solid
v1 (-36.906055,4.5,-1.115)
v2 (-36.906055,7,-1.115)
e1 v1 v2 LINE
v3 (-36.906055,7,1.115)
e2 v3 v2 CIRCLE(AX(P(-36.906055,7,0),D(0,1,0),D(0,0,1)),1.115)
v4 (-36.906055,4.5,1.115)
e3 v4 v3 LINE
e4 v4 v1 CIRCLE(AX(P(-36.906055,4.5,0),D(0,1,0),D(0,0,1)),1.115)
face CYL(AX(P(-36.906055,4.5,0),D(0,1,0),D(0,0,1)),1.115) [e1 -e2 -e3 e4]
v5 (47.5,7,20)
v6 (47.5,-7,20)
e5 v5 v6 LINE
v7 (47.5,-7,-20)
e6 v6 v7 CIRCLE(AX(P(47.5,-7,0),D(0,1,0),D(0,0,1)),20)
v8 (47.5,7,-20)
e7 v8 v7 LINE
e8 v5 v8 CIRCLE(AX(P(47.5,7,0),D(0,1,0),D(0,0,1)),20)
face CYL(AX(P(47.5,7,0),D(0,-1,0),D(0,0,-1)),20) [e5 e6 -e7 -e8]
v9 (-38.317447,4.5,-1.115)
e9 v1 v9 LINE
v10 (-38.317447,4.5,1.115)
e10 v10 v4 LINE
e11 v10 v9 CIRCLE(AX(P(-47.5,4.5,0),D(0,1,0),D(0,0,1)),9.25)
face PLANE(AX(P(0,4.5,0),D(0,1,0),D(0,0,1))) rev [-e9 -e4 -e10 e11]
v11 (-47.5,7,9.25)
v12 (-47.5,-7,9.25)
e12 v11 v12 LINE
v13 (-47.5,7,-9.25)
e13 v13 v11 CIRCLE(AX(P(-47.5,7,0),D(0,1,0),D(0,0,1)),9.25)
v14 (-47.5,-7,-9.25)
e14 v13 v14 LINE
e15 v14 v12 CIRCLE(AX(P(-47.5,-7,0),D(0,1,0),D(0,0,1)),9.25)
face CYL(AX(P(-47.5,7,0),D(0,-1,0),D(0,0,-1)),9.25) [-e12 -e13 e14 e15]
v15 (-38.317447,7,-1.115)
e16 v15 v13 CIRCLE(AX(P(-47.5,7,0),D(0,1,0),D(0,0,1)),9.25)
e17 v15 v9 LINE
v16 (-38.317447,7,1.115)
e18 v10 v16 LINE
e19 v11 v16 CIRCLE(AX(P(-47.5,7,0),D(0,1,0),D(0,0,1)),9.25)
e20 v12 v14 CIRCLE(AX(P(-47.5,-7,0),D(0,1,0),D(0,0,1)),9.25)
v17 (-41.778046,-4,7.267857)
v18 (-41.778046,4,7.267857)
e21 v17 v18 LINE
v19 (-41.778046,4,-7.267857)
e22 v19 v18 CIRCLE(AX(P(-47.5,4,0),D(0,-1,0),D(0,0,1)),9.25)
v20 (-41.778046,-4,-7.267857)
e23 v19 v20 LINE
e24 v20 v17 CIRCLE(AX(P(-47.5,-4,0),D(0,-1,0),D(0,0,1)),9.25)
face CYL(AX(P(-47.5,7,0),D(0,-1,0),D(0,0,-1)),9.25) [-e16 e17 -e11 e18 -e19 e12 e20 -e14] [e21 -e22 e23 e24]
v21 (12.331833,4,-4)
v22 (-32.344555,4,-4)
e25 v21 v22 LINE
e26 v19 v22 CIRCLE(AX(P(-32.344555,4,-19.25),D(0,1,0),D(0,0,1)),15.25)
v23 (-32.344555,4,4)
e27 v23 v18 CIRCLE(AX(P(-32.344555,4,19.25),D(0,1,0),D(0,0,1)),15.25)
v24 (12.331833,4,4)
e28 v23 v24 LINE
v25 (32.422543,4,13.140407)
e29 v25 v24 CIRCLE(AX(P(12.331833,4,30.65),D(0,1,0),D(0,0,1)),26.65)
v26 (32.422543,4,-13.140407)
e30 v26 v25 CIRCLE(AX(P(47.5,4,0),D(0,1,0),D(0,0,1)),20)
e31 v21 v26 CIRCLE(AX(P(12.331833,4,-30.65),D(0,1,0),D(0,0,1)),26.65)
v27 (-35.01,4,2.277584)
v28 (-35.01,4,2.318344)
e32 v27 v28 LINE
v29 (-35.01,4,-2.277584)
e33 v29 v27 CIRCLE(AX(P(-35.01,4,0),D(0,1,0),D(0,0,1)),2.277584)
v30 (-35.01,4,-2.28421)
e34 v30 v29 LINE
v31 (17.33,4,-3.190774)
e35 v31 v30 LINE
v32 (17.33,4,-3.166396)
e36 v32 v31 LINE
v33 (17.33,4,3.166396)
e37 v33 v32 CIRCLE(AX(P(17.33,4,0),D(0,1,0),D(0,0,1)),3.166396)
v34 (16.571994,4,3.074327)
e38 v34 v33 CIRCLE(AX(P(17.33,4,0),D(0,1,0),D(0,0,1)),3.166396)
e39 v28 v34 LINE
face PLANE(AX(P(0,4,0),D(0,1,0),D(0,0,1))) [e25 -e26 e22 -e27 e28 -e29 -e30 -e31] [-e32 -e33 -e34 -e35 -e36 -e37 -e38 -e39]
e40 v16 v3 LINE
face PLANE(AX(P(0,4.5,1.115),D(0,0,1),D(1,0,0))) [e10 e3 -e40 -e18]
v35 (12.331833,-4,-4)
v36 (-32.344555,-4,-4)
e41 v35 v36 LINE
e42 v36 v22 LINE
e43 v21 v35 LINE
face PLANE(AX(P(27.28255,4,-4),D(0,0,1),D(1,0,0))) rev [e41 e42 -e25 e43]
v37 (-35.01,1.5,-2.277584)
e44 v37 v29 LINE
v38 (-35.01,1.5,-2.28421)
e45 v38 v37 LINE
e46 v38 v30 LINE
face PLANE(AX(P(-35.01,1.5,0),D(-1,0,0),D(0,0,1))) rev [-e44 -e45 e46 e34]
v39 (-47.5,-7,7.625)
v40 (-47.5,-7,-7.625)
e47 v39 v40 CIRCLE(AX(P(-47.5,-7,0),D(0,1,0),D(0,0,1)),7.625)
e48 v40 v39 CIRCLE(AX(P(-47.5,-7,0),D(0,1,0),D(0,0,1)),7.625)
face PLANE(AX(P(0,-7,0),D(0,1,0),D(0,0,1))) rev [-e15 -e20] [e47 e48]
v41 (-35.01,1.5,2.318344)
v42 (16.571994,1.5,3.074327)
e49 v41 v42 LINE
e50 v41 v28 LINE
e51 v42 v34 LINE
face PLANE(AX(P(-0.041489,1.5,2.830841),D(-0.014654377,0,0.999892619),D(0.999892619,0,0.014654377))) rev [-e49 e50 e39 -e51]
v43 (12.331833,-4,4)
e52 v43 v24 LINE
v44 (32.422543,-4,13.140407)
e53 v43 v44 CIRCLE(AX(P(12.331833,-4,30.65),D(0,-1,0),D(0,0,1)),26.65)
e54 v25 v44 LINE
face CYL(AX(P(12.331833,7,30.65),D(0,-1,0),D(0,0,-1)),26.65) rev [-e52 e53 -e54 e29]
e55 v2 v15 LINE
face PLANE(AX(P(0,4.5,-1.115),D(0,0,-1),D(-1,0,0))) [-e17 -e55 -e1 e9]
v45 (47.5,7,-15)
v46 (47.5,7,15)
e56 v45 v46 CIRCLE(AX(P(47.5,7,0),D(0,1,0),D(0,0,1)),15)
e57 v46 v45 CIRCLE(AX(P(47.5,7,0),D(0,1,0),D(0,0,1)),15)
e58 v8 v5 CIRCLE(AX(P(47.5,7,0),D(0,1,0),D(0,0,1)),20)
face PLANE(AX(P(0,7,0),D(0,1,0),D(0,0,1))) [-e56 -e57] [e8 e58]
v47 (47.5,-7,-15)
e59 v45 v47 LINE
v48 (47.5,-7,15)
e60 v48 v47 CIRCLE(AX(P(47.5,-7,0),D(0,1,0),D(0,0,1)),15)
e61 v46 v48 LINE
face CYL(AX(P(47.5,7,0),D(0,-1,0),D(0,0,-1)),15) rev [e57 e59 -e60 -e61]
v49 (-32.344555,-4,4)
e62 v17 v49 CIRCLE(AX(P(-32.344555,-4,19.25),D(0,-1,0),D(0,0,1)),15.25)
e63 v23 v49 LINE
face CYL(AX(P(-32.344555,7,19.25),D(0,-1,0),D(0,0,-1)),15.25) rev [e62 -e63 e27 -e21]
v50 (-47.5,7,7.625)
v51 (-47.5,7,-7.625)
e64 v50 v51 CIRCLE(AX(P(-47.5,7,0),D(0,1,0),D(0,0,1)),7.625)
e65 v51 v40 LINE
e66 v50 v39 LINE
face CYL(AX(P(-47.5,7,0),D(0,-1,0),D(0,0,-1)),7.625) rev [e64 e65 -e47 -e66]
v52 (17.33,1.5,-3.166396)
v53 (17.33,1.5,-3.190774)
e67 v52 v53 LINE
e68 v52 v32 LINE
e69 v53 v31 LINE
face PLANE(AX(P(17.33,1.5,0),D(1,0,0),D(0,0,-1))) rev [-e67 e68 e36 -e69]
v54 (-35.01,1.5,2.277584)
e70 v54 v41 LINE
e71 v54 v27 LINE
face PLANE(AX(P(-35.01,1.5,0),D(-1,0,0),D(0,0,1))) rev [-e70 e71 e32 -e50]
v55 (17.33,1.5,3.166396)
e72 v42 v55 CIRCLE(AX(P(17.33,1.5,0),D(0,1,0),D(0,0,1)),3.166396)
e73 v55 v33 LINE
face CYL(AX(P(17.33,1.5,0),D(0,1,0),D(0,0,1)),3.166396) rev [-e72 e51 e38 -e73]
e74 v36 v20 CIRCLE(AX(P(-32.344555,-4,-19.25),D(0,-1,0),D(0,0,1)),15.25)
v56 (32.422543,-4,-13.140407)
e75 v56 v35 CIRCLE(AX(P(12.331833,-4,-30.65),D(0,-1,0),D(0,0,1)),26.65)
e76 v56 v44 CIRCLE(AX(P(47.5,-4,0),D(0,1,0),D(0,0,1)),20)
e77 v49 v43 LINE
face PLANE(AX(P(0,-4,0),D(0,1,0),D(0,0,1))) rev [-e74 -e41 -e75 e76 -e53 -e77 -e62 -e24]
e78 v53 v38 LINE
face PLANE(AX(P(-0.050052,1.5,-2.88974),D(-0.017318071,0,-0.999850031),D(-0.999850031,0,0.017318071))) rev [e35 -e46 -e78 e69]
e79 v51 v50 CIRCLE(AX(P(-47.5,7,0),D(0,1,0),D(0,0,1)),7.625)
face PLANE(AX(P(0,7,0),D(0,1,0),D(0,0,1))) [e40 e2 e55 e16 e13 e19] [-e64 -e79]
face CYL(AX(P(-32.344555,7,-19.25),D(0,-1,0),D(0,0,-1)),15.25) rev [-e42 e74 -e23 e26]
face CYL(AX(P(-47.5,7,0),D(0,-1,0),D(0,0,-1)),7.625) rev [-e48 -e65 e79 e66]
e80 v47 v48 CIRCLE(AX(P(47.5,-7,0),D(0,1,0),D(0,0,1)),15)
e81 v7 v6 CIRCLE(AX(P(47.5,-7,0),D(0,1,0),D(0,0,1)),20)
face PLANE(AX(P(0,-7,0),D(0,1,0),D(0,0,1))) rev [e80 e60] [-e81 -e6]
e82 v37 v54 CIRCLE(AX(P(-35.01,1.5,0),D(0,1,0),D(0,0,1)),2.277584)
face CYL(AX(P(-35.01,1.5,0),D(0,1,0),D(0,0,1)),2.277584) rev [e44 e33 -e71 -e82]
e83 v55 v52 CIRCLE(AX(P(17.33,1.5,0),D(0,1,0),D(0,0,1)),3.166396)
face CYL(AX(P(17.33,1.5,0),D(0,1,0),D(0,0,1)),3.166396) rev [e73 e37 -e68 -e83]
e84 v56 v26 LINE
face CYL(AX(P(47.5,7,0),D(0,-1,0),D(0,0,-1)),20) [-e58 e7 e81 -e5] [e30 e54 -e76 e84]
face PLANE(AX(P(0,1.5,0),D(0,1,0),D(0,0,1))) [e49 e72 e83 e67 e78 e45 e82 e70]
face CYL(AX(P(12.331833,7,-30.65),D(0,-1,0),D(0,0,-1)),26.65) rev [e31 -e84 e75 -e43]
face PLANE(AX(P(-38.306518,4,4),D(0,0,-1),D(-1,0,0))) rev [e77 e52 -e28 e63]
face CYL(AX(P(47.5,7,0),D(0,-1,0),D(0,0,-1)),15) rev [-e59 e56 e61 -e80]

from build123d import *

# Parameters (mm, degrees)
BIG_END_EYE_SKETCH_R        = 20
BIG_END_EYE_SKETCH_R_2      = 15
BIG_END_EYE_40_DEPTH        = 7
SMALL_END_EYE_SKETCH_R      = 9.25
SMALL_END_EYE_SKETCH_R_2    = 7.625
SMALL_END_EYE_18_5_DEPTH    = 7
SHANK_DEPTH                 = 4
BIG_END_BLEND_R26_65_A_R    = 26.65
SMALL_END_BLEND_R15_25_A_R  = 15.25
SMALL_END_BLEND_R15_25_B_R  = 15.25
BIG_END_BLEND_R26_65_B_R    = 26.65
SHANK_RECESS_2_5_DEEP_DEPTH = 2.5
SHANK_PAD_2_5_DEPTH         = 2.5


with BuildPart() as part:
    # Big End Eye Sketch → Big End Eye Ø40 (new, symmetric)
    with BuildSketch(Plane(origin=(0, 0, 0), x_dir=(1, 0, 0), z_dir=(0, 1, 0))):
        with Locations(Location((47.5, 0, 0), (0, 0, 270))):
            Circle(BIG_END_EYE_SKETCH_R)
        with Locations(Location((47.5, 0, 0), (0, 0, 270))):
            Circle(BIG_END_EYE_SKETCH_R_2, mode=Mode.SUBTRACT)
    extrude(amount=BIG_END_EYE_40_DEPTH, both=True)



with BuildPart() as body_2:
    # Small End Eye Sketch → Small End Eye Ø18.5 (new, symmetric)
    with BuildSketch(Plane(origin=(0, 0, 0), x_dir=(1, 0, 0), z_dir=(0, 1, 0))):
        with Locations(Location((-47.5, 0, 0), (0, 0, 270))):
            Circle(SMALL_END_EYE_SKETCH_R)
        with Locations(Location((-47.5, 0, 0), (0, 0, 270))):
            Circle(SMALL_END_EYE_SKETCH_R_2, mode=Mode.SUBTRACT)
    extrude(amount=SMALL_END_EYE_18_5_DEPTH, both=True)


with BuildPart() as part_1:
    add(part.part)

    add(body_2.part)  # Shank merges body 2
    # Shank Profile Sketch → Shank (add, symmetric)
    with BuildSketch(Plane(origin=(0, 0, 0), x_dir=(1, 0, 0), z_dir=(0, 1, 0))):
        Polygon((27.282550476, 4), (28.047385708, 4), (28.047385708, -4), (-38.306518326, -4), (-39.375179325, -4), (-39.375179325, 4), align=None)
    extrude(amount=SHANK_DEPTH, both=True)

    # Big End Blend R26.65 A
    big_end_blend_r26_65_a_edges = [part_1.edges().sort_by_distance(p)[0] for p in [
        (27.904082058, 0, -4),
    ]]
    fillet(big_end_blend_r26_65_a_edges, radius=BIG_END_BLEND_R26_65_A_R)

    # Small End Blend R15.25 A
    small_end_blend_r15_25_a_edges = [part_1.edges().sort_by_distance(p)[0] for p in [
        (-39.159586341, 0, -4),
    ]]
    fillet(small_end_blend_r15_25_a_edges, radius=SMALL_END_BLEND_R15_25_A_R)

    # Small End Blend R15.25 B
    small_end_blend_r15_25_b_edges = [part_1.edges().sort_by_distance(p)[0] for p in [
        (-39.159586341, 0, 4),
    ]]
    fillet(small_end_blend_r15_25_b_edges, radius=SMALL_END_BLEND_R15_25_B_R)

    # Big End Blend R26.65 B
    big_end_blend_r26_65_b_edges = [part_1.edges().sort_by_distance(p)[0] for p in [
        (27.904082058, 0, 4),
    ]]
    fillet(big_end_blend_r26_65_b_edges, radius=BIG_END_BLEND_R26_65_B_R)

    # Shank Recess Sketch → Shank Recess 2.5 Deep (cut)
    with BuildSketch(Plane(origin=(0, 4, 0), x_dir=(1, 0, 0), z_dir=(0, 1, 0))):
        with BuildLine():
            ThreePointArc((-35.01, 2.277583754), (-37.287583754, 0), (-35.01, -2.277583754))
            Line((-35.01, -2.277583754), (-35.01, -2.318344298))
            Line((-35.01, -2.318344298), (16.571994255, -3.074327461))
            ThreePointArc((16.571994255, -3.074327461), (20.473294407, -0.381788318), (17.33, 3.16639575))
            Line((17.33, 3.16639575), (17.33, 3.190774264))
            Line((17.33, 3.190774264), (-35.01, 2.28421045))
            Line((-35.01, 2.28421045), (-35.01, 2.277583754))
        make_face()
    extrude(amount=-SHANK_RECESS_2_5_DEEP_DEPTH, mode=Mode.SUBTRACT)

    # Shank Pad Sketch → Shank Pad 2.5 (add)
    with BuildSketch(Plane(origin=(0, 7, 0), x_dir=(1, 0, 0), z_dir=(0, 1, 0))):
        with BuildLine():
            Line((-38.413384426, 0), (-36.90605517, 0))
            Line((-36.90605517, 0), (-35.79105517, 0))
            ThreePointArc((-35.79105517, 0), (-36.117631109, 0.788424061), (-36.90605517, 1.115))
            Line((-36.90605517, 1.115), (-38.413384426, 1.115))
            Line((-38.413384426, 1.115), (-38.413384426, 0))
        make_face()
        with BuildLine():
            Line((-35.79105517, 0), (-36.90605517, 0))
            Line((-36.90605517, 0), (-38.413384426, 0))
            Line((-38.413384426, 0), (-38.413384426, -1.115))
            Line((-38.413384426, -1.115), (-36.90605517, -1.115))
            ThreePointArc((-36.90605517, -1.115), (-36.117631109, -0.788424061), (-35.79105517, 0))
        make_face()
    extrude(amount=-SHANK_PAD_2_5_DEPTH)


solid = part_1.part
